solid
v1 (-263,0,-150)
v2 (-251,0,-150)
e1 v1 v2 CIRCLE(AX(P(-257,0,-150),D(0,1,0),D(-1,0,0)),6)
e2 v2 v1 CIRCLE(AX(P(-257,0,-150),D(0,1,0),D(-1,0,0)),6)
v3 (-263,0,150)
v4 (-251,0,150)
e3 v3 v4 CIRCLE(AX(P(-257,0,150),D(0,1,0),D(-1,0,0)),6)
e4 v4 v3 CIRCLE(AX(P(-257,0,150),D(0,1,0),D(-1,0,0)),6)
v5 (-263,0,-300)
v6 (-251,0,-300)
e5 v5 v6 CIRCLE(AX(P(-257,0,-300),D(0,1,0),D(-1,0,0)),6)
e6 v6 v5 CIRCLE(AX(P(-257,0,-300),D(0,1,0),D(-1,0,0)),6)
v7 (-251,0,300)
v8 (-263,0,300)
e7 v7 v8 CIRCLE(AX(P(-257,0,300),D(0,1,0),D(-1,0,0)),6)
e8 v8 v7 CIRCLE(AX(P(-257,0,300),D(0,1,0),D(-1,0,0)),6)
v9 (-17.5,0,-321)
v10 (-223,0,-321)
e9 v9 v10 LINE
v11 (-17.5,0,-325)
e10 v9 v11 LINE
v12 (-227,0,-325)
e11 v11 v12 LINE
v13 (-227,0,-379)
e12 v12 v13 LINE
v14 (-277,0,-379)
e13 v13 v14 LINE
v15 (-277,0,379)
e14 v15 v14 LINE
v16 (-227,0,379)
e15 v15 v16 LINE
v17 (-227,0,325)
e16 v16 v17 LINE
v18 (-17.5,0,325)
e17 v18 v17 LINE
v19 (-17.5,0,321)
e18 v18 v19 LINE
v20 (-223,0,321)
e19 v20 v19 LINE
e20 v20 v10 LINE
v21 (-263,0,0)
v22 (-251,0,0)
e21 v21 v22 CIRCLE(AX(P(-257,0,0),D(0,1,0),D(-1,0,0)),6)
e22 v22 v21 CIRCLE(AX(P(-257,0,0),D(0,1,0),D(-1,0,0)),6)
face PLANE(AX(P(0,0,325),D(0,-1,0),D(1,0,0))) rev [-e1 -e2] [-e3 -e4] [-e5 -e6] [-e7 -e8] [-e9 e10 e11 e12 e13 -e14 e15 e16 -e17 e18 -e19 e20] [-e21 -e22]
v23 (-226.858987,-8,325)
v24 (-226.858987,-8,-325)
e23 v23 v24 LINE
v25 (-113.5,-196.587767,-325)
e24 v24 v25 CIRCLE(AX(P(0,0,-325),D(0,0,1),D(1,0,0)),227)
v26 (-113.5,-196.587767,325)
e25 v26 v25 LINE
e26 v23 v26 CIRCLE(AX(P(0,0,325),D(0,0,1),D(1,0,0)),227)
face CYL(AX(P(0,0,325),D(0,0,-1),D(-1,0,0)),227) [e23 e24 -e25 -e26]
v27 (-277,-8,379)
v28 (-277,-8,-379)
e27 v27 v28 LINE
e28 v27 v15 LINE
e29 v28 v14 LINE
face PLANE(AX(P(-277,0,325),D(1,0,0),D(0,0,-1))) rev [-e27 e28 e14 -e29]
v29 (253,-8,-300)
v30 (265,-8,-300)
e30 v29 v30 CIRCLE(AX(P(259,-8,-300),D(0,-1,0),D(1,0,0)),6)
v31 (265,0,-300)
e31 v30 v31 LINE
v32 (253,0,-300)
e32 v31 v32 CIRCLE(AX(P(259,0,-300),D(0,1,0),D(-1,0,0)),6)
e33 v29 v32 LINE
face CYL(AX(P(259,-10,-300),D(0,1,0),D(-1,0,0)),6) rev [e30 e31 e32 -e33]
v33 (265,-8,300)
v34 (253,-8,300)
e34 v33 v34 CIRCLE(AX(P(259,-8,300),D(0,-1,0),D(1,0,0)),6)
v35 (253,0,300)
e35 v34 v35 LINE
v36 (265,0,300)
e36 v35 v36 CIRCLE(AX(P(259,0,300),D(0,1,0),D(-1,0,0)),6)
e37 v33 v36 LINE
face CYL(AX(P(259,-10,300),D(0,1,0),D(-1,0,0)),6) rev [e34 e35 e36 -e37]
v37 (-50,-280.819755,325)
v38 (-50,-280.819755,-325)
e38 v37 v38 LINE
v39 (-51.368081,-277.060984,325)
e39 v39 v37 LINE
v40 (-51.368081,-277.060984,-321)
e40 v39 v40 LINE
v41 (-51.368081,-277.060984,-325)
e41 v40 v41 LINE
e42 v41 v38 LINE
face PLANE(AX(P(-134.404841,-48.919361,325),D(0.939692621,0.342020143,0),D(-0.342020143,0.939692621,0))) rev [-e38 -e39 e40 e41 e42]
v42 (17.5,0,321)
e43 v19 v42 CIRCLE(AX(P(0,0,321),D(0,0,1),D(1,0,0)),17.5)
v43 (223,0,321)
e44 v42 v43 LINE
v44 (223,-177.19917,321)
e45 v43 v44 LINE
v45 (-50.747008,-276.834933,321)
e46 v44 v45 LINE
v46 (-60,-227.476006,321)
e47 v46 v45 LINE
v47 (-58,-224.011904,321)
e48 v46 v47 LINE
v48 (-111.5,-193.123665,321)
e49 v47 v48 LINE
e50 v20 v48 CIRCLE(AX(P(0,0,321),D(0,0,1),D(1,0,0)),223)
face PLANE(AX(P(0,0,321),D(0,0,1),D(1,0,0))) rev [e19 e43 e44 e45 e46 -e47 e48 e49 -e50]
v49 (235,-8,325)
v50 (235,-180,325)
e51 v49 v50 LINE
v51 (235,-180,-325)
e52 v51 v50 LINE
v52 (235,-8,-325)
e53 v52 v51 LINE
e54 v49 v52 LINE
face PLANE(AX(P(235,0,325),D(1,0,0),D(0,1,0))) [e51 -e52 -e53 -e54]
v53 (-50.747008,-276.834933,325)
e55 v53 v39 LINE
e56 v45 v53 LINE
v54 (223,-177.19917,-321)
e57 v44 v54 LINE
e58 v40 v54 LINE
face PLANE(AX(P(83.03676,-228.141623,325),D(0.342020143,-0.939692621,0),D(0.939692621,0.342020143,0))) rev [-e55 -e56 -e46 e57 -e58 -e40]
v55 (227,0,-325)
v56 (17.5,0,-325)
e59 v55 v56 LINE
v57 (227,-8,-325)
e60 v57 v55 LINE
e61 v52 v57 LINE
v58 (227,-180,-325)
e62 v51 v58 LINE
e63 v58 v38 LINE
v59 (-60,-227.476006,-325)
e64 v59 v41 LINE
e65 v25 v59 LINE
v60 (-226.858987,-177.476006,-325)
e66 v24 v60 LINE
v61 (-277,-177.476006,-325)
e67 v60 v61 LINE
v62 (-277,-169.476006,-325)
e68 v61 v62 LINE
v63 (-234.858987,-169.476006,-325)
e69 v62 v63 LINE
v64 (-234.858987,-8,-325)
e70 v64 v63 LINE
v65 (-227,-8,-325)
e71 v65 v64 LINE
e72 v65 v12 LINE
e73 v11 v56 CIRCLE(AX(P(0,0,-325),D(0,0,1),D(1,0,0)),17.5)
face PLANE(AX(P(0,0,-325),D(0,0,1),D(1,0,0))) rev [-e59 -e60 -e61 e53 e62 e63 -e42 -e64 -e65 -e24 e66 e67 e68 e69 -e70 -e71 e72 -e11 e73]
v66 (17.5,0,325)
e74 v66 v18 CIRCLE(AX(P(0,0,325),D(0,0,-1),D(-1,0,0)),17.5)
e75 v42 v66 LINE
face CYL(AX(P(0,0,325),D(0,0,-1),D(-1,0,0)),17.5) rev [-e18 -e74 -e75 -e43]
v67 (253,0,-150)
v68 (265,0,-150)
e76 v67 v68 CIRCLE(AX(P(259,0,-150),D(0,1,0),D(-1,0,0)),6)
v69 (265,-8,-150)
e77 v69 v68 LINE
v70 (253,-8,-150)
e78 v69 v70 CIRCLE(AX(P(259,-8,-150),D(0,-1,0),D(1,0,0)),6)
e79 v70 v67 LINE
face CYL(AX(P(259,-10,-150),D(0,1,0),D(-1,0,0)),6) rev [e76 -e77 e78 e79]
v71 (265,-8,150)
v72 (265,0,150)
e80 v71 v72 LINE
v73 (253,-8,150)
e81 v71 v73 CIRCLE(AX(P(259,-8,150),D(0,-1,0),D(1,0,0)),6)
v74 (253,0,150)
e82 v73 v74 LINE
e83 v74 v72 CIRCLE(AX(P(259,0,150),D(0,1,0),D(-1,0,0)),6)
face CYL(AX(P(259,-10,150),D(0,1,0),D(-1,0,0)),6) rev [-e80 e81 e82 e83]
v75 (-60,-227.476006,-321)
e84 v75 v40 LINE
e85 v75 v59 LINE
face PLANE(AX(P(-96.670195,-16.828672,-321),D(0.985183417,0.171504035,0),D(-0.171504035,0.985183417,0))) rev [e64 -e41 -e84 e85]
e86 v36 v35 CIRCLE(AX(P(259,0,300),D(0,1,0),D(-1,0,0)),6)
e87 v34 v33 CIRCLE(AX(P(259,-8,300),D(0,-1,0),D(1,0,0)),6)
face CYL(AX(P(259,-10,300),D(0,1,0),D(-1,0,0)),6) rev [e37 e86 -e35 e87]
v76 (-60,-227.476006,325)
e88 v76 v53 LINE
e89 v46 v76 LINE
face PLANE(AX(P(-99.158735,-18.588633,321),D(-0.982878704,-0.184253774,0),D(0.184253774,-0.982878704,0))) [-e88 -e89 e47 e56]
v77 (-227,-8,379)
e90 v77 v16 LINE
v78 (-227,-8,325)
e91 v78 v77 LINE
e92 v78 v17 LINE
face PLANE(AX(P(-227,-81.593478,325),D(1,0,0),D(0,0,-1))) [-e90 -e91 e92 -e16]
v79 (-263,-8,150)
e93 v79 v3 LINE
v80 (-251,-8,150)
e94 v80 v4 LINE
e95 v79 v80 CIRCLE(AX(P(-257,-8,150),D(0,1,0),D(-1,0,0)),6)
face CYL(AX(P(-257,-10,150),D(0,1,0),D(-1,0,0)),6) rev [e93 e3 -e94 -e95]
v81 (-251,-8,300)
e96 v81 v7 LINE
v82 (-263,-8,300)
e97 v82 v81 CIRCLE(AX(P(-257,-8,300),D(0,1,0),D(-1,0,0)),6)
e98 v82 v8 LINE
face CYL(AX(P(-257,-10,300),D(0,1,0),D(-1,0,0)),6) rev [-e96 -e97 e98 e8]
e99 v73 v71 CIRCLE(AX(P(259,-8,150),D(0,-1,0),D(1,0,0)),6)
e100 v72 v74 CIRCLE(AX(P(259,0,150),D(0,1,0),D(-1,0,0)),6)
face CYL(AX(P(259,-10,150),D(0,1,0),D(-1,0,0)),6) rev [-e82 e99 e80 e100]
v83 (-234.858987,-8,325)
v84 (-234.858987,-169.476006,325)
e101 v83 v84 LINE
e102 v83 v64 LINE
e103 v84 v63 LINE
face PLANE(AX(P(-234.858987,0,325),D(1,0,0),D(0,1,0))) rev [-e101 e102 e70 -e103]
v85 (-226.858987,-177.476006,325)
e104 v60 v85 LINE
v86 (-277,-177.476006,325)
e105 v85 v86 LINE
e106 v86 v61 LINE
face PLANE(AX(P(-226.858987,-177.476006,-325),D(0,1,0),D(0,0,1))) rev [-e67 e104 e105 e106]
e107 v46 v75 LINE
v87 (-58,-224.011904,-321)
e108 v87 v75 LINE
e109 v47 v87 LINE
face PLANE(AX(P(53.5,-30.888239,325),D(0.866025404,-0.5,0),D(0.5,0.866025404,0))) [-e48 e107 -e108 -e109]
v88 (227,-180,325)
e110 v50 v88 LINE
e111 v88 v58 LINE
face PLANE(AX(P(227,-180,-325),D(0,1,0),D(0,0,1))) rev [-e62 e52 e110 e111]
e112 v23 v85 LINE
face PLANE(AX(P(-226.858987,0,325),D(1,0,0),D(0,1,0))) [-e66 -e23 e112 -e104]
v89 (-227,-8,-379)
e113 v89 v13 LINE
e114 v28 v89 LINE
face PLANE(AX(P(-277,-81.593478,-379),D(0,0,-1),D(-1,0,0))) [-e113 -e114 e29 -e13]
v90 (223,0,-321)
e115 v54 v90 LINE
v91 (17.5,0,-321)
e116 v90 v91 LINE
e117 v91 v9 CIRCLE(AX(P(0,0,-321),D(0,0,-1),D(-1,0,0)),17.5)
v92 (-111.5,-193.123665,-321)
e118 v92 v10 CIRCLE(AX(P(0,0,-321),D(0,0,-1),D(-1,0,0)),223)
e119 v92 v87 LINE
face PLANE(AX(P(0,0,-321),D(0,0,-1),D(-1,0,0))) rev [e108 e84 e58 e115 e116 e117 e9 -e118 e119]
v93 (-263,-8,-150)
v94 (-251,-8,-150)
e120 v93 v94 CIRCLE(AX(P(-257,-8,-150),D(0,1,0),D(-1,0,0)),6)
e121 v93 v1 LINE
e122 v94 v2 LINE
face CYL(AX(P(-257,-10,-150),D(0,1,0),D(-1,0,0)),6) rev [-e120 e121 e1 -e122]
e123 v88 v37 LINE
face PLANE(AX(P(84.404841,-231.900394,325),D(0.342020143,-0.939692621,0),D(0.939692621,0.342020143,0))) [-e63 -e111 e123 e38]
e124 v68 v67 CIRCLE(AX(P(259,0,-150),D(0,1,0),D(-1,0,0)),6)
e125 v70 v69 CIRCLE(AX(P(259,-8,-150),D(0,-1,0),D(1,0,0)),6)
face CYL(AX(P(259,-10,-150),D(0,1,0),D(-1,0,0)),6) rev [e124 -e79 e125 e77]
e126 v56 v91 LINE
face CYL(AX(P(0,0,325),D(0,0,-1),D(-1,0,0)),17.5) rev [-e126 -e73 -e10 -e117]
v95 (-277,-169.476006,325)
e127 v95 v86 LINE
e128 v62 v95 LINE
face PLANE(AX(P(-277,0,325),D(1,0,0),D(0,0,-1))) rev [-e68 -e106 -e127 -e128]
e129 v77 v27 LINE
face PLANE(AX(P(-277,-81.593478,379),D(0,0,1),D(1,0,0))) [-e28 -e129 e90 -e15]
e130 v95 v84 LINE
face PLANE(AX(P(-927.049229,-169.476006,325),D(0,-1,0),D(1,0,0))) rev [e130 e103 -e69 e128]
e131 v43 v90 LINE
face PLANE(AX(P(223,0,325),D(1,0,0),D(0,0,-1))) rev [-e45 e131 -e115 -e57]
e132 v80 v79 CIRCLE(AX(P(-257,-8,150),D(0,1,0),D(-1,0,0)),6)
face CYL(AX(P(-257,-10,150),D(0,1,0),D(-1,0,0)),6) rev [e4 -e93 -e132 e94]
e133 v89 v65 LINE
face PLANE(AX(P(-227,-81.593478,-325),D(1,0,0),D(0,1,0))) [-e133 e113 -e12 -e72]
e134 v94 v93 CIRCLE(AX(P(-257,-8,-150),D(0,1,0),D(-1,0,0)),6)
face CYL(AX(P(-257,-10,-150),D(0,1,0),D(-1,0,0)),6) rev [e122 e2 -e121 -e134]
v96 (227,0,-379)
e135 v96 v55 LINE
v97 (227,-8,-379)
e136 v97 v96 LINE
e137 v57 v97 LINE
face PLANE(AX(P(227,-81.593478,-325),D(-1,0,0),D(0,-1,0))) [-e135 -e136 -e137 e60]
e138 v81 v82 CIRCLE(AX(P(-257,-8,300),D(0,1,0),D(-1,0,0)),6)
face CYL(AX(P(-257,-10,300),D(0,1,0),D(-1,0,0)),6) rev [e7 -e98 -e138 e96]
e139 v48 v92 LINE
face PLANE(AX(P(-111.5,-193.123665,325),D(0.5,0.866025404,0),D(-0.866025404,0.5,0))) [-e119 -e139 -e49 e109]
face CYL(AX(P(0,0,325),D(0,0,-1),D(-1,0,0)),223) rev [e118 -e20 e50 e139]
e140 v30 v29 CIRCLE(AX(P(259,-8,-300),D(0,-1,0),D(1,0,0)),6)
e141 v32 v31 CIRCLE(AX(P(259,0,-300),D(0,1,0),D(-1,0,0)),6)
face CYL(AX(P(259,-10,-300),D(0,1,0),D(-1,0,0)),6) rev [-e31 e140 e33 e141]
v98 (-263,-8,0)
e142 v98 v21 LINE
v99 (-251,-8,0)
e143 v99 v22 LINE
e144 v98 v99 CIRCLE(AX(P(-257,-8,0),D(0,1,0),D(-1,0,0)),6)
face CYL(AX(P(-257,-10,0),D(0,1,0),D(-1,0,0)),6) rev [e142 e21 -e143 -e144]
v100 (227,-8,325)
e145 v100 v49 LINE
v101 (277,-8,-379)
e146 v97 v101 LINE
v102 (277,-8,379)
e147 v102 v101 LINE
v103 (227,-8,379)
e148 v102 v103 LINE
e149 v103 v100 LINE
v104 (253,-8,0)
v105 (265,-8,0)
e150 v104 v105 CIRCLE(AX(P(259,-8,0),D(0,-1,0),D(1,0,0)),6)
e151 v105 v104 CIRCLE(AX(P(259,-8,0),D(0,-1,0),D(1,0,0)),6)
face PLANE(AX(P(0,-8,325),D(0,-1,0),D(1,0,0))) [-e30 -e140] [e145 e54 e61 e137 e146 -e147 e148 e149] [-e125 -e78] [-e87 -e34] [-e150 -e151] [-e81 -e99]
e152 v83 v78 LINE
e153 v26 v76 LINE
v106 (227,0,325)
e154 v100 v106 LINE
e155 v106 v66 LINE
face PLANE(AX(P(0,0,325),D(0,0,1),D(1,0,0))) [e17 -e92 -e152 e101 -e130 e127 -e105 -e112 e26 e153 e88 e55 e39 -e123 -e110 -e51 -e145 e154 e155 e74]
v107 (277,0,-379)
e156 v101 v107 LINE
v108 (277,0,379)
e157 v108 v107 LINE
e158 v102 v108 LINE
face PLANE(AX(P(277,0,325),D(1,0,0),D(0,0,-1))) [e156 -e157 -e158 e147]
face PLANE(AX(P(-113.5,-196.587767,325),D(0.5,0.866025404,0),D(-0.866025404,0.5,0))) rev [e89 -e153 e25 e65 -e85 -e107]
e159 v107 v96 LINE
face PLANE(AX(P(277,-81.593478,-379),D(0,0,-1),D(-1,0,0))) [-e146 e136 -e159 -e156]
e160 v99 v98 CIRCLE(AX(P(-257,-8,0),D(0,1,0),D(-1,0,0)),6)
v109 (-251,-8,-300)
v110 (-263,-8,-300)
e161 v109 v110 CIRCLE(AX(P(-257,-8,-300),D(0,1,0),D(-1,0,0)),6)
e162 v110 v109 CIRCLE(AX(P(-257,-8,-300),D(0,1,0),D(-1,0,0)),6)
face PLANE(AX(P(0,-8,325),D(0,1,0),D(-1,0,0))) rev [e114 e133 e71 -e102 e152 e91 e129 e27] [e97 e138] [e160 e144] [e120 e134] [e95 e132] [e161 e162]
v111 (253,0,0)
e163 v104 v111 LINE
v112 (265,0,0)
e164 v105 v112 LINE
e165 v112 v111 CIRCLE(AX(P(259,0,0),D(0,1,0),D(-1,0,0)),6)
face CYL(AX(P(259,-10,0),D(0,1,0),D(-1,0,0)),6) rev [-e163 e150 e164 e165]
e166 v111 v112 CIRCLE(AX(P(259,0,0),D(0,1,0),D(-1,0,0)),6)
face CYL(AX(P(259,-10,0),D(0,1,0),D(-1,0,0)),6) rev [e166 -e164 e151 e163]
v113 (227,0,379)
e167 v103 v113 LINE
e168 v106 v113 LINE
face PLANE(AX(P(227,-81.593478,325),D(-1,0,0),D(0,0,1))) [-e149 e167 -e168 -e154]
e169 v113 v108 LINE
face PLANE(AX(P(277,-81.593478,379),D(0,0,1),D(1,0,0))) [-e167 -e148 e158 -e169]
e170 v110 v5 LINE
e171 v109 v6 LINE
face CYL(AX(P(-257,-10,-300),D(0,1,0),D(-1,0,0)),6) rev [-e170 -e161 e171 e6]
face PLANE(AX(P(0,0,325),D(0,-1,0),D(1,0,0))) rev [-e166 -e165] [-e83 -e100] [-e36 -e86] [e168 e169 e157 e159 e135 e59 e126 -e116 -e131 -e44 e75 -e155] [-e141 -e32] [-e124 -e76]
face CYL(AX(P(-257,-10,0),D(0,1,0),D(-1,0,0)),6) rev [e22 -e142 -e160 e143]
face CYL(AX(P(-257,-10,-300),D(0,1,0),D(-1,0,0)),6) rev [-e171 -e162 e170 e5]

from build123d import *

# Parameters (mm, degrees)
BOSS_EXTRUDE2_DEPTH       = 325
BOSS_EXTRUDE2_2_DEPTH     = 325
BOSS_EXTRUDE3_DEPTH       = 4
BOSS_EXTRUDE4_START       = -4
BOSS_EXTRUDE4_DEPTH       = 4
SKETCH5_R                 = 6
CUT_EXTRUDE1_DEPTH        = 10
LPATTERN1_COUNT           = 3
LPATTERN1_PITCH           = 150
LPATTERN2_COPY_1_SKETCH_R = 6
LPATTERN2_COPY_1_DEPTH    = 10
LPATTERN2_COPY_2_SKETCH_R = 6
LPATTERN2_COPY_2_DEPTH    = 10
LPATTERN2_COPY_3_SKETCH_R = 6
LPATTERN2_COPY_3_DEPTH    = 10
LPATTERN2_COPY_4_SKETCH_R = 6
LPATTERN2_COPY_4_DEPTH    = 10
LPATTERN2_COPY_5_SKETCH_R = 6
LPATTERN2_COPY_5_DEPTH    = 10
LPATTERN2_COPY_6_SKETCH_R = 6
LPATTERN2_COPY_6_DEPTH    = 10
CUT_EXTRUDE2_DEPTH        = 762.052386329
CUT_EXTRUDE2_DEPTH_BACK   = 762.052386329
SKETCH6_R                 = 17.5
CUT_EXTRUDE3_DEPTH        = 762.052386329
CUT_EXTRUDE3_DEPTH_BACK   = 762.052386329
SKETCH7_W                 = 100.370226039
SKETCH7_H                 = 50
SKETCH8_W                 = 650
SKETCH8_H                 = 8
BOSS_EXTRUDE5_DEPTH       = 42.141012962
CUT_EXTRUDE4_DEPTH        = 762.052386329
CUT_EXTRUDE4_DEPTH_BACK   = 762.052386329
SKETCH9_W                 = 99.024260435
SKETCH9_H                 = 85.798945111
SKETCH10_W                = 50
SKETCH10_H                = 54
BOSS_EXTRUDE6_DEPTH       = 8


with BuildPart() as part:
    # Sketch1 → Boss-Extrude2 (new, symmetric)
    with BuildSketch(Plane.XY):
        with BuildLine():
            Line((-223, 0), (-277, 0))
            Line((-277, 0), (-277, -8))
            Line((-277, -8), (-234.858987038, -8))
            Line((-234.858987038, -8), (-234.858987038, -219.476006061))
            Line((-234.858987038, -219.476006061), (-278.858987038, -219.476006061))
            Line((-278.858987038, -219.476006061), (-278.858987038, -227.476006061))
            Line((-278.858987038, -227.476006061), (-226.858987038, -227.476006061))
            Line((-226.858987038, -227.476006061), (-226.858987038, -8))
            ThreePointArc((-226.858987038, -8), (-194.556923413, -116.947011728), (-113.5, -196.587766659))
            Line((-113.5, -196.587766659), (-60, -227.476006061))
            Line((-60, -227.476006061), (-58, -224.011904446))
            Line((-58, -224.011904446), (-111.5, -193.123665044))
            ThreePointArc((-111.5, -193.123665044), (-193.123665044, -111.5), (-223, 0))
        make_face()
    extrude(amount=BOSS_EXTRUDE2_DEPTH, both=True)



with BuildPart() as body_2:
    # Sketch1 → Boss-Extrude2 2 (new, symmetric)
    with BuildSketch(Plane.XY):
        Polygon((277, 0), (223, 0), (223, -177.199169847), (-51.368080573, -277.060984409), (-50, -280.819754892), (227, -180), (227, -227.476006061), (279, -227.476006061), (279, -219.476006061), (235, -219.476006061), (235, -8), (277, -8), align=None)
    extrude(amount=BOSS_EXTRUDE2_2_DEPTH, both=True)


with BuildPart() as part_1:
    add(part.part)

    add(body_2.part)  # Boss-Extrude3 merges body 2
    # Sketch3 → Boss-Extrude3 (add)
    with BuildSketch(Plane.XY.offset(325)):
        with BuildLine():
            Line((-58, -224.011904446), (-60, -227.476006061))
            Line((-60, -227.476006061), (84.865527782, -227.476006061))
            Line((84.865527782, -227.476006061), (223, -177.199169847))
            Line((223, -177.199169847), (223, 0))
            Line((223, 0), (-223, 0))
            ThreePointArc((-223, 0), (-193.123665044, -111.5), (-111.5, -193.123665044))
            Line((-111.5, -193.123665044), (-58, -224.011904446))
        make_face()
        Polygon((84.865527782, -227.476006061), (-60, -227.476006061), (-50.747008298, -276.834932587), align=None)
    extrude(amount=-BOSS_EXTRUDE3_DEPTH)

    # Sketch4 → Boss-Extrude4 (add)
    with BuildSketch(Plane(origin=(0, 0, -325), x_dir=(-1, 0, 0), z_dir=(0, 0, -1)).offset(BOSS_EXTRUDE4_START)):
        with BuildLine():
            Line((111.5, -193.123665044), (58, -224.011904446))
            Line((58, -224.011904446), (60, -227.476006061))
            Line((60, -227.476006061), (51.368080573, -277.060984409))
            Line((51.368080573, -277.060984409), (-223, -177.199169847))
            Line((-223, -177.199169847), (-223, 0))
            Line((-223, 0), (223, 0))
            ThreePointArc((223, 0), (193.123665044, -111.5), (111.5, -193.123665044))
        make_face()
    extrude(amount=BOSS_EXTRUDE4_DEPTH)

    # Sketch5 → Cut-Extrude1 (cut)
    with BuildSketch(Plane(origin=(0, 0, 0), x_dir=(1, 0, 0), z_dir=(0, 1, 0))):
        with Locations(Location((-257, 0, 0), (0, 0, 180))):
            Circle(SKETCH5_R)
        with Locations(Location((259, 0, 0), (0, 0, 180))):
            Circle(SKETCH5_R)
    cut_extrude1 = extrude(amount=-CUT_EXTRUDE1_DEPTH, mode=Mode.SUBTRACT)

    # LPattern1: Cut-Extrude1 ×3
    with Locations(*[(0, 0, -i * LPATTERN1_PITCH) for i in range(1, LPATTERN1_COUNT)]):
        add(cut_extrude1, mode=Mode.SUBTRACT)

    # LPattern2 copy 1 sketch → LPattern2 copy 1 (cut)
    with BuildSketch(Plane(origin=(0, 0, 0), x_dir=(1, 0, 0), z_dir=(0, 1, 0))):
        with Locations(Location((-257, 0, 0), (0, 0, 180))):
            Circle(LPATTERN2_COPY_1_SKETCH_R)
        with Locations(Location((259, 0, 0), (0, 0, 180))):
            Circle(LPATTERN2_COPY_1_SKETCH_R)
    extrude(amount=-LPATTERN2_COPY_1_DEPTH, mode=Mode.SUBTRACT)

    # LPattern2 copy 2 sketch → LPattern2 copy 2 (cut)
    with BuildSketch(Plane(origin=(0, 0, 150), x_dir=(1, 0, 0), z_dir=(0, 1, 0))):
        with Locations(Location((-257, 0, 0), (0, 0, 180))):
            Circle(LPATTERN2_COPY_2_SKETCH_R)
        with Locations(Location((259, 0, 0), (0, 0, 180))):
            Circle(LPATTERN2_COPY_2_SKETCH_R)
    extrude(amount=-LPATTERN2_COPY_2_DEPTH, mode=Mode.SUBTRACT)

    # LPattern2 copy 3 sketch → LPattern2 copy 3 (cut)
    with BuildSketch(Plane(origin=(0, 0, -150), x_dir=(1, 0, 0), z_dir=(0, 1, 0))):
        with Locations(Location((-257, 0, 0), (0, 0, 180))):
            Circle(LPATTERN2_COPY_3_SKETCH_R)
        with Locations(Location((259, 0, 0), (0, 0, 180))):
            Circle(LPATTERN2_COPY_3_SKETCH_R)
    extrude(amount=-LPATTERN2_COPY_3_DEPTH, mode=Mode.SUBTRACT)

    # LPattern2 copy 4 sketch → LPattern2 copy 4 (cut)
    with BuildSketch(Plane(origin=(0, 0, 0), x_dir=(1, 0, 0), z_dir=(0, 1, 0))):
        with Locations(Location((-257, 0, 0), (0, 0, 180))):
            Circle(LPATTERN2_COPY_4_SKETCH_R)
        with Locations(Location((259, 0, 0), (0, 0, 180))):
            Circle(LPATTERN2_COPY_4_SKETCH_R)
    extrude(amount=-LPATTERN2_COPY_4_DEPTH, mode=Mode.SUBTRACT)

    # LPattern2 copy 5 sketch → LPattern2 copy 5 (cut)
    with BuildSketch(Plane(origin=(0, 0, 150), x_dir=(1, 0, 0), z_dir=(0, 1, 0))):
        with Locations(Location((-257, 0, 0), (0, 0, 180))):
            Circle(LPATTERN2_COPY_5_SKETCH_R)
        with Locations(Location((259, 0, 0), (0, 0, 180))):
            Circle(LPATTERN2_COPY_5_SKETCH_R)
    extrude(amount=-LPATTERN2_COPY_5_DEPTH, mode=Mode.SUBTRACT)

    # LPattern2 copy 6 sketch → LPattern2 copy 6 (cut)
    with BuildSketch(Plane(origin=(0, 0, 300), x_dir=(1, 0, 0), z_dir=(0, 1, 0))):
        with Locations(Location((-257, 0, 0), (0, 0, 180))):
            Circle(LPATTERN2_COPY_6_SKETCH_R)
        with Locations(Location((259, 0, 0), (0, 0, 180))):
            Circle(LPATTERN2_COPY_6_SKETCH_R)
    extrude(amount=-LPATTERN2_COPY_6_DEPTH, mode=Mode.SUBTRACT)

    # Sketch6 → Cut-Extrude2 (cut, two sides: drawn at the far end of the back side and taken through both)
    with BuildSketch(Plane(origin=(0, 0, -325), x_dir=(-1, 0, 0), z_dir=(0, 0, -1)).offset(-CUT_EXTRUDE2_DEPTH_BACK)):
        Circle(SKETCH6_R)
    extrude(amount=CUT_EXTRUDE2_DEPTH + CUT_EXTRUDE2_DEPTH_BACK, mode=Mode.SUBTRACT)

    # Sketch7 → Cut-Extrude3 (cut, two sides: drawn at the far end of the back side and taken through both)
    with BuildSketch(Plane.XY.offset(325).offset(-CUT_EXTRUDE3_DEPTH_BACK)):
        with Locations((-277.044100058, -202.476006061)):
            Rectangle(SKETCH7_W, SKETCH7_H)
    extrude(amount=CUT_EXTRUDE3_DEPTH + CUT_EXTRUDE3_DEPTH_BACK, mode=Mode.SUBTRACT)

    # Sketch8 → Boss-Extrude5 (add)
    with BuildSketch(Plane.ZY.offset(234.858987038)):
        with Locations((0, -173.476006061)):
            Rectangle(SKETCH8_W, SKETCH8_H)
    extrude(amount=BOSS_EXTRUDE5_DEPTH)

    # Sketch9 → Cut-Extrude4 (cut, two sides: drawn at the far end of the back side and taken through both)
    with BuildSketch(Plane.XY.offset(325).offset(-CUT_EXTRUDE4_DEPTH_BACK)):
        with Locations((276.512130218, -222.899472556)):
            Rectangle(SKETCH9_W, SKETCH9_H)
    extrude(amount=CUT_EXTRUDE4_DEPTH + CUT_EXTRUDE4_DEPTH_BACK, mode=Mode.SUBTRACT)

    # Sketch10 → Boss-Extrude6 (add)
    with BuildSketch(Plane(origin=(0, 0, 0), x_dir=(1, 0, 0), z_dir=(0, 1, 0))):
        with Locations((-252, 352)):
            Rectangle(SKETCH10_W, SKETCH10_H)
        with Locations((252, 352)):
            Rectangle(SKETCH10_W, SKETCH10_H)
        with Locations((252, -352)):
            Rectangle(SKETCH10_W, SKETCH10_H)
        with Locations((-252, -352)):
            Rectangle(SKETCH10_W, SKETCH10_H)
    extrude(amount=-BOSS_EXTRUDE6_DEPTH)


solid = part_1.part
